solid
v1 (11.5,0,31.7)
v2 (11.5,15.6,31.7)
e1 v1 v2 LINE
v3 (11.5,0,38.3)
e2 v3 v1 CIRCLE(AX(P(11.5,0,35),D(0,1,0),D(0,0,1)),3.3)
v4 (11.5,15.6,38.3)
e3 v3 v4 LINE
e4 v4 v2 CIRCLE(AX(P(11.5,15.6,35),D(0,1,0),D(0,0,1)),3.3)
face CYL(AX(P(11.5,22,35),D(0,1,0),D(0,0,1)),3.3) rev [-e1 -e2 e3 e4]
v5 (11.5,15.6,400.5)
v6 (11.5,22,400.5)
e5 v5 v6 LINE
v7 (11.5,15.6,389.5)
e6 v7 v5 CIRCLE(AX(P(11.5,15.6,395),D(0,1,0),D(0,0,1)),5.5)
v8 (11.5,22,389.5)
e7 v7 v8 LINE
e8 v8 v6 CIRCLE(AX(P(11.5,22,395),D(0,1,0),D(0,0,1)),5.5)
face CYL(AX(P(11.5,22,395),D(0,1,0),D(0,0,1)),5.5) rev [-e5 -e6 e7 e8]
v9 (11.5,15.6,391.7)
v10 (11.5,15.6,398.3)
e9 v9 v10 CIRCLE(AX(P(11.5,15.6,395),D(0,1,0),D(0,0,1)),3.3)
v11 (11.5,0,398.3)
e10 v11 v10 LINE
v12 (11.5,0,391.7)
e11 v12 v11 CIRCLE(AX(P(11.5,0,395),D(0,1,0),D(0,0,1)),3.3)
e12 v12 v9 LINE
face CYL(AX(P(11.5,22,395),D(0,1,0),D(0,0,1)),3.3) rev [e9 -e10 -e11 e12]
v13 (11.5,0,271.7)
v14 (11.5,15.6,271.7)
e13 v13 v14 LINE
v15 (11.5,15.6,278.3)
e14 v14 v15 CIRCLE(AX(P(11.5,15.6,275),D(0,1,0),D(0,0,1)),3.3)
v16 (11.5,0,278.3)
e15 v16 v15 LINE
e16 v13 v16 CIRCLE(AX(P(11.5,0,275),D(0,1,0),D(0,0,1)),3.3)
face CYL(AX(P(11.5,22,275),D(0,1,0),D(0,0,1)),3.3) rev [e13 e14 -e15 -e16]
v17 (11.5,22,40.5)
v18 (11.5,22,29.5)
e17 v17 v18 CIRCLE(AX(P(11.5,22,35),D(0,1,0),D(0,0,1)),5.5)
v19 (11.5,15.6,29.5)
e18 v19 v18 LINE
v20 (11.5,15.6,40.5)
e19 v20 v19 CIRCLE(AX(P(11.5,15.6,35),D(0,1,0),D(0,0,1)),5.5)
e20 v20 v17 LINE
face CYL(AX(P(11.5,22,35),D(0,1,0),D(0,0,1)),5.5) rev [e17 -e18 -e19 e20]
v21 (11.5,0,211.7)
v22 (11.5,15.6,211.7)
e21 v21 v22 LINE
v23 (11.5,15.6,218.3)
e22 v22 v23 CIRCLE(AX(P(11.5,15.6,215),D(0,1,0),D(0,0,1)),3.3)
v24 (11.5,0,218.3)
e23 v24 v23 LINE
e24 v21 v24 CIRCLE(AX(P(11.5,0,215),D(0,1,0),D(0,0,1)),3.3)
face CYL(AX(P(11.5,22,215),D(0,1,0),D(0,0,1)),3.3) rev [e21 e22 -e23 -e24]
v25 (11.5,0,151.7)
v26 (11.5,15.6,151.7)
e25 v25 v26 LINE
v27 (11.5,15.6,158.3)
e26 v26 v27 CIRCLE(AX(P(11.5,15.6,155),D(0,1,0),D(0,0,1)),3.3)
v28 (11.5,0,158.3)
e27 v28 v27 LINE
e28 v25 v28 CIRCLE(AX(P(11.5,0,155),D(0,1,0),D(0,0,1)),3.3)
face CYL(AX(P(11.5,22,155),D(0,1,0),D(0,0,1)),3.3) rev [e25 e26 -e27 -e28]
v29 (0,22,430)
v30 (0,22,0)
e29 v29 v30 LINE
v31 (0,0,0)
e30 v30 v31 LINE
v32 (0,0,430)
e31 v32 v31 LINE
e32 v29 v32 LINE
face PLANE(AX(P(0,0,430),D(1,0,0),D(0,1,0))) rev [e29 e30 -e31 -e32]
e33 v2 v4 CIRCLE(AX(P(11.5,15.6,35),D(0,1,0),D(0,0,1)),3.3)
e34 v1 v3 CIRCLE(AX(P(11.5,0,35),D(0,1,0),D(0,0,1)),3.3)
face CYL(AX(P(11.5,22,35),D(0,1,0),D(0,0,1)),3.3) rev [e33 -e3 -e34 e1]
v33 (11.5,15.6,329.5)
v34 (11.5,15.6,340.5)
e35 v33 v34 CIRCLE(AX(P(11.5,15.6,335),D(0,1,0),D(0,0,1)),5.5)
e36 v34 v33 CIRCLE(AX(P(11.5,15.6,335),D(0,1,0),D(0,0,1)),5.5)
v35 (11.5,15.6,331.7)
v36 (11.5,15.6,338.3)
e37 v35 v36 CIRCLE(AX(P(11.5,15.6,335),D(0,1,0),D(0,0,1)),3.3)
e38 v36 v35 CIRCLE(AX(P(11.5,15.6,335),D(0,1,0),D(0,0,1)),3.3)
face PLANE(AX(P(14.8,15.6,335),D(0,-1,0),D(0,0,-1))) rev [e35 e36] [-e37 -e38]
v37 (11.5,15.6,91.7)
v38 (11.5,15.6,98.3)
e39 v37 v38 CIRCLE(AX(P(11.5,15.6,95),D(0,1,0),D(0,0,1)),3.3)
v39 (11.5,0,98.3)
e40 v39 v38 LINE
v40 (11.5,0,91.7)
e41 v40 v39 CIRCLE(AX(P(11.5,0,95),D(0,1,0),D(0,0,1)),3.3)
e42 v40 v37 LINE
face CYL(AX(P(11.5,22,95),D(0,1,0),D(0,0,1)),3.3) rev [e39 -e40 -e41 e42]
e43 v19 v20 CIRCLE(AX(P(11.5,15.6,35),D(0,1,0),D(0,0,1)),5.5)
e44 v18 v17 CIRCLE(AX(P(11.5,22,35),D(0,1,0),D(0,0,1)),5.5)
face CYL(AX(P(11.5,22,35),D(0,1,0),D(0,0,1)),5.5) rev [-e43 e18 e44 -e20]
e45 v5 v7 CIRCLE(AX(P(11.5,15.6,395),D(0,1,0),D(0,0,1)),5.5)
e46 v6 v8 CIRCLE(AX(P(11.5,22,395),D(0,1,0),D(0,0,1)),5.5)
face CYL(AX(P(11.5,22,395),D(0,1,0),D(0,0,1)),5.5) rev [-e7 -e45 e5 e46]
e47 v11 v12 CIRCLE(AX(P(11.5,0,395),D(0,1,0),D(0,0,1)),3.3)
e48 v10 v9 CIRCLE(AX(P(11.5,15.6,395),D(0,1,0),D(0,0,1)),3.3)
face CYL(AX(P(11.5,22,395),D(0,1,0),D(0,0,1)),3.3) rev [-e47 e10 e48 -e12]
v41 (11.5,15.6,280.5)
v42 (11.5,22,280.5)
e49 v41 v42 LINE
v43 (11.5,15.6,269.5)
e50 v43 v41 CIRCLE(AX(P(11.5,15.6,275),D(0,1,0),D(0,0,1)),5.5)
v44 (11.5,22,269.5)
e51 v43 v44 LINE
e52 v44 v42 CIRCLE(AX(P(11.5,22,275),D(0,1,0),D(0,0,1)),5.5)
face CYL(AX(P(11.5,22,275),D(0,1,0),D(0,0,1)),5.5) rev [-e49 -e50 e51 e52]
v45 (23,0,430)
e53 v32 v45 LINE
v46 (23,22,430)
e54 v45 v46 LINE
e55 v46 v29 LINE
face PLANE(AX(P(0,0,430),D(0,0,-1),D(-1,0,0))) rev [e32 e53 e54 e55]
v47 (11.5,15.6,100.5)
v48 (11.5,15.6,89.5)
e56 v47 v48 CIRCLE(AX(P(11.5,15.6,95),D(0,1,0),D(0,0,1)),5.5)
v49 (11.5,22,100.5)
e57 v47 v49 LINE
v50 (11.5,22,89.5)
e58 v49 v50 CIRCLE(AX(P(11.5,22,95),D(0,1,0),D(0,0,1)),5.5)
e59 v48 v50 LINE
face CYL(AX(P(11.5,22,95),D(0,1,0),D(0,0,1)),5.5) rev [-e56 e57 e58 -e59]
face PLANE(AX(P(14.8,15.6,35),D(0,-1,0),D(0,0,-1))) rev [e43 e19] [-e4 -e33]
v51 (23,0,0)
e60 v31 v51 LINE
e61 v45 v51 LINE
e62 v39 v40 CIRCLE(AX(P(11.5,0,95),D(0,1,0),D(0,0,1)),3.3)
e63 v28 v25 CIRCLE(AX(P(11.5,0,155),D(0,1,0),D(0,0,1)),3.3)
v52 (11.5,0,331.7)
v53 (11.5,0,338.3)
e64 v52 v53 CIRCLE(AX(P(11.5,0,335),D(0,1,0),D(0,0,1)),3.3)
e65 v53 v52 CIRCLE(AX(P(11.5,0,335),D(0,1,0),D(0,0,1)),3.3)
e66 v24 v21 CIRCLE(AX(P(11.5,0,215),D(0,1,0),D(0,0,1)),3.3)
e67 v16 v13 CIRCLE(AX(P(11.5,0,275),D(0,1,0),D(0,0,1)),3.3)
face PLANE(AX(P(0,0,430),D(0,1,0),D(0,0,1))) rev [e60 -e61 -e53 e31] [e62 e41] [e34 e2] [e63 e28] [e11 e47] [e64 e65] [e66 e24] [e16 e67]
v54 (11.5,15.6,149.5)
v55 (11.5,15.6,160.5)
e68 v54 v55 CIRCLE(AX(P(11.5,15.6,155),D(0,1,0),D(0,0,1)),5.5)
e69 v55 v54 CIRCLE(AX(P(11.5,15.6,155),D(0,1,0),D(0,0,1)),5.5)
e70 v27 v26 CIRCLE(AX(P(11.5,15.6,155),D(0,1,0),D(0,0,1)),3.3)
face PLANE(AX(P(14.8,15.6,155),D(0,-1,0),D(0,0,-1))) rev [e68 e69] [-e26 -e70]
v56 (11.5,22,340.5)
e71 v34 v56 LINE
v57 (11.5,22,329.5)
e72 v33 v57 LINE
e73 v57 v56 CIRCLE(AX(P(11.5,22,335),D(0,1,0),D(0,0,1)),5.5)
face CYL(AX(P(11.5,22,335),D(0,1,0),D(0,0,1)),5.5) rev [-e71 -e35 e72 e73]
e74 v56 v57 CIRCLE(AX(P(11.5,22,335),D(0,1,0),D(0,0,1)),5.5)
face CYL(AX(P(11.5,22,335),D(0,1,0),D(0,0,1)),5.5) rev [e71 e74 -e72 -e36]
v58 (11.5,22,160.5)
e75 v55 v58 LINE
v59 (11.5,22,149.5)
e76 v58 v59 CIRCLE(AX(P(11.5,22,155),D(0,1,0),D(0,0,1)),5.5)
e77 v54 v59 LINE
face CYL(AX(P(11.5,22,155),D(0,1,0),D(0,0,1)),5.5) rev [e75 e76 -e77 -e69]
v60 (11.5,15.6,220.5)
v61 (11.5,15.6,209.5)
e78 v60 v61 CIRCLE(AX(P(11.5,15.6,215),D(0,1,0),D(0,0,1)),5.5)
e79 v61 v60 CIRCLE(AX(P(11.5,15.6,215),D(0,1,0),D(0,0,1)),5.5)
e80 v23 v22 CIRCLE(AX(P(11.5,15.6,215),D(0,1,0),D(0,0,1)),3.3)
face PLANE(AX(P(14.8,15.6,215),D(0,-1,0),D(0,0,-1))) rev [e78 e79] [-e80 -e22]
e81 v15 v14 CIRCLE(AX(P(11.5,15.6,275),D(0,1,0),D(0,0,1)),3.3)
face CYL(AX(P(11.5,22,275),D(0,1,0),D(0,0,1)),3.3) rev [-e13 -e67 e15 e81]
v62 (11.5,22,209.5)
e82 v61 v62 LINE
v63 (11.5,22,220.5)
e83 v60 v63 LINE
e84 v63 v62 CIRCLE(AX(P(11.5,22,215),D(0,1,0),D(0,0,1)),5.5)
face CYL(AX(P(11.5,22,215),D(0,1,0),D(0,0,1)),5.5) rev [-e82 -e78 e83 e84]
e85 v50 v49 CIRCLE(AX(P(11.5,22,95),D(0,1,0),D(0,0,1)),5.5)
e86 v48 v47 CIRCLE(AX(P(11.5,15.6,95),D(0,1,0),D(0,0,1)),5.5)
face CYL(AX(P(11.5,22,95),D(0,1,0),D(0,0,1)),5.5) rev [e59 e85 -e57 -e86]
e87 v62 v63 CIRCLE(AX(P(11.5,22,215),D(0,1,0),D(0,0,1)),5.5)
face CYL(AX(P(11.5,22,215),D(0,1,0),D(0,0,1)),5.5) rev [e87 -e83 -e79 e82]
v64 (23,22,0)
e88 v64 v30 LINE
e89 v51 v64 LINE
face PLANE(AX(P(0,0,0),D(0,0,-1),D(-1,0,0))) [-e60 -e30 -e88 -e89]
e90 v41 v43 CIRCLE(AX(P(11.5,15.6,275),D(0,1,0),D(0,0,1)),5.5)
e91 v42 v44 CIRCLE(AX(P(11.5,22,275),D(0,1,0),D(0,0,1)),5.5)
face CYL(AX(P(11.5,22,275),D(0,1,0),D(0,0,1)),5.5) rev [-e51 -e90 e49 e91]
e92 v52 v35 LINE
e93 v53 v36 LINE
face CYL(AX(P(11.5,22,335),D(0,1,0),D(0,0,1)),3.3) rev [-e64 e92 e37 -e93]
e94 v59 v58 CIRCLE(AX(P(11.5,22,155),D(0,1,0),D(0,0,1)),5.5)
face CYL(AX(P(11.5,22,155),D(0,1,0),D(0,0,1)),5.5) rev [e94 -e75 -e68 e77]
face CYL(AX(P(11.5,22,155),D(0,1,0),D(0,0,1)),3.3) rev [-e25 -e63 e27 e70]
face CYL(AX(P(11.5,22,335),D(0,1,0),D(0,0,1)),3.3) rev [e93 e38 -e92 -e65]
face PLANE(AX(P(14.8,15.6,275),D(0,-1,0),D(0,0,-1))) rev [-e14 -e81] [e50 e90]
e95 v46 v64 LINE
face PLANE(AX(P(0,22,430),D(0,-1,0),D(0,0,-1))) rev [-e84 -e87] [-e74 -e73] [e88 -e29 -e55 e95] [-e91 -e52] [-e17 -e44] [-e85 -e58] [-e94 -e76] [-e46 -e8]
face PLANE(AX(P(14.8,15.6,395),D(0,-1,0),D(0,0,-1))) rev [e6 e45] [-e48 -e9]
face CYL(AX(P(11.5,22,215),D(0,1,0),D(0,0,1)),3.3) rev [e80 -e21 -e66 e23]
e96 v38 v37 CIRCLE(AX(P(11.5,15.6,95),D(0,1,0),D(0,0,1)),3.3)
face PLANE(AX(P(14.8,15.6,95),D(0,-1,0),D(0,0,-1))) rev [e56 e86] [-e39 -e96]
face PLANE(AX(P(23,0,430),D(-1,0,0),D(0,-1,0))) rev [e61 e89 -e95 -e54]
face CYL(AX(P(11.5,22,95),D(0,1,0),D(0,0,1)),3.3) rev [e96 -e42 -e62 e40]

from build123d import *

# Parameters (mm, degrees)
SKETCH_1_W                   = 23
SKETCH_1_H                   = 22
EXTRUDE_1_DEPTH              = 430
HOLE_WIZARD_M6_1_D           = 6.6
HOLE_WIZARD_M6_1_CBORE_D     = 11
HOLE_WIZARD_M6_1_CBORE_DEPTH = 6.4
PATTERN_LINEAR_1_COUNT       = 7
PATTERN_LINEAR_1_PITCH       = 60


with BuildPart() as part:
    # 草图1 → 凸台-拉伸1 (new body)
    with BuildSketch(Plane.XY):
        with Locations((11.5, 11)):
            Rectangle(SKETCH_1_W, SKETCH_1_H)
    extrude(amount=EXTRUDE_1_DEPTH)

    # M6 六角凹头螺钉的柱形沉头孔1 (through all)
    with Locations(Plane(origin=(0, 22, 0), x_dir=(1, 0, 0), z_dir=(0, 1, 0))):
        with Locations((11.5, -395)):
            hole_wizard_m6_1 = CounterBoreHole(HOLE_WIZARD_M6_1_D / 2, HOLE_WIZARD_M6_1_CBORE_D / 2, HOLE_WIZARD_M6_1_CBORE_DEPTH)

    # 阵列(线性)1: M6 六角凹头螺钉的柱形沉头孔1 ×7
    with Locations(*[(0, 0, -i * PATTERN_LINEAR_1_PITCH) for i in range(1, PATTERN_LINEAR_1_COUNT)]):
        add(hole_wizard_m6_1, mode=Mode.SUBTRACT)


solid = part.part
